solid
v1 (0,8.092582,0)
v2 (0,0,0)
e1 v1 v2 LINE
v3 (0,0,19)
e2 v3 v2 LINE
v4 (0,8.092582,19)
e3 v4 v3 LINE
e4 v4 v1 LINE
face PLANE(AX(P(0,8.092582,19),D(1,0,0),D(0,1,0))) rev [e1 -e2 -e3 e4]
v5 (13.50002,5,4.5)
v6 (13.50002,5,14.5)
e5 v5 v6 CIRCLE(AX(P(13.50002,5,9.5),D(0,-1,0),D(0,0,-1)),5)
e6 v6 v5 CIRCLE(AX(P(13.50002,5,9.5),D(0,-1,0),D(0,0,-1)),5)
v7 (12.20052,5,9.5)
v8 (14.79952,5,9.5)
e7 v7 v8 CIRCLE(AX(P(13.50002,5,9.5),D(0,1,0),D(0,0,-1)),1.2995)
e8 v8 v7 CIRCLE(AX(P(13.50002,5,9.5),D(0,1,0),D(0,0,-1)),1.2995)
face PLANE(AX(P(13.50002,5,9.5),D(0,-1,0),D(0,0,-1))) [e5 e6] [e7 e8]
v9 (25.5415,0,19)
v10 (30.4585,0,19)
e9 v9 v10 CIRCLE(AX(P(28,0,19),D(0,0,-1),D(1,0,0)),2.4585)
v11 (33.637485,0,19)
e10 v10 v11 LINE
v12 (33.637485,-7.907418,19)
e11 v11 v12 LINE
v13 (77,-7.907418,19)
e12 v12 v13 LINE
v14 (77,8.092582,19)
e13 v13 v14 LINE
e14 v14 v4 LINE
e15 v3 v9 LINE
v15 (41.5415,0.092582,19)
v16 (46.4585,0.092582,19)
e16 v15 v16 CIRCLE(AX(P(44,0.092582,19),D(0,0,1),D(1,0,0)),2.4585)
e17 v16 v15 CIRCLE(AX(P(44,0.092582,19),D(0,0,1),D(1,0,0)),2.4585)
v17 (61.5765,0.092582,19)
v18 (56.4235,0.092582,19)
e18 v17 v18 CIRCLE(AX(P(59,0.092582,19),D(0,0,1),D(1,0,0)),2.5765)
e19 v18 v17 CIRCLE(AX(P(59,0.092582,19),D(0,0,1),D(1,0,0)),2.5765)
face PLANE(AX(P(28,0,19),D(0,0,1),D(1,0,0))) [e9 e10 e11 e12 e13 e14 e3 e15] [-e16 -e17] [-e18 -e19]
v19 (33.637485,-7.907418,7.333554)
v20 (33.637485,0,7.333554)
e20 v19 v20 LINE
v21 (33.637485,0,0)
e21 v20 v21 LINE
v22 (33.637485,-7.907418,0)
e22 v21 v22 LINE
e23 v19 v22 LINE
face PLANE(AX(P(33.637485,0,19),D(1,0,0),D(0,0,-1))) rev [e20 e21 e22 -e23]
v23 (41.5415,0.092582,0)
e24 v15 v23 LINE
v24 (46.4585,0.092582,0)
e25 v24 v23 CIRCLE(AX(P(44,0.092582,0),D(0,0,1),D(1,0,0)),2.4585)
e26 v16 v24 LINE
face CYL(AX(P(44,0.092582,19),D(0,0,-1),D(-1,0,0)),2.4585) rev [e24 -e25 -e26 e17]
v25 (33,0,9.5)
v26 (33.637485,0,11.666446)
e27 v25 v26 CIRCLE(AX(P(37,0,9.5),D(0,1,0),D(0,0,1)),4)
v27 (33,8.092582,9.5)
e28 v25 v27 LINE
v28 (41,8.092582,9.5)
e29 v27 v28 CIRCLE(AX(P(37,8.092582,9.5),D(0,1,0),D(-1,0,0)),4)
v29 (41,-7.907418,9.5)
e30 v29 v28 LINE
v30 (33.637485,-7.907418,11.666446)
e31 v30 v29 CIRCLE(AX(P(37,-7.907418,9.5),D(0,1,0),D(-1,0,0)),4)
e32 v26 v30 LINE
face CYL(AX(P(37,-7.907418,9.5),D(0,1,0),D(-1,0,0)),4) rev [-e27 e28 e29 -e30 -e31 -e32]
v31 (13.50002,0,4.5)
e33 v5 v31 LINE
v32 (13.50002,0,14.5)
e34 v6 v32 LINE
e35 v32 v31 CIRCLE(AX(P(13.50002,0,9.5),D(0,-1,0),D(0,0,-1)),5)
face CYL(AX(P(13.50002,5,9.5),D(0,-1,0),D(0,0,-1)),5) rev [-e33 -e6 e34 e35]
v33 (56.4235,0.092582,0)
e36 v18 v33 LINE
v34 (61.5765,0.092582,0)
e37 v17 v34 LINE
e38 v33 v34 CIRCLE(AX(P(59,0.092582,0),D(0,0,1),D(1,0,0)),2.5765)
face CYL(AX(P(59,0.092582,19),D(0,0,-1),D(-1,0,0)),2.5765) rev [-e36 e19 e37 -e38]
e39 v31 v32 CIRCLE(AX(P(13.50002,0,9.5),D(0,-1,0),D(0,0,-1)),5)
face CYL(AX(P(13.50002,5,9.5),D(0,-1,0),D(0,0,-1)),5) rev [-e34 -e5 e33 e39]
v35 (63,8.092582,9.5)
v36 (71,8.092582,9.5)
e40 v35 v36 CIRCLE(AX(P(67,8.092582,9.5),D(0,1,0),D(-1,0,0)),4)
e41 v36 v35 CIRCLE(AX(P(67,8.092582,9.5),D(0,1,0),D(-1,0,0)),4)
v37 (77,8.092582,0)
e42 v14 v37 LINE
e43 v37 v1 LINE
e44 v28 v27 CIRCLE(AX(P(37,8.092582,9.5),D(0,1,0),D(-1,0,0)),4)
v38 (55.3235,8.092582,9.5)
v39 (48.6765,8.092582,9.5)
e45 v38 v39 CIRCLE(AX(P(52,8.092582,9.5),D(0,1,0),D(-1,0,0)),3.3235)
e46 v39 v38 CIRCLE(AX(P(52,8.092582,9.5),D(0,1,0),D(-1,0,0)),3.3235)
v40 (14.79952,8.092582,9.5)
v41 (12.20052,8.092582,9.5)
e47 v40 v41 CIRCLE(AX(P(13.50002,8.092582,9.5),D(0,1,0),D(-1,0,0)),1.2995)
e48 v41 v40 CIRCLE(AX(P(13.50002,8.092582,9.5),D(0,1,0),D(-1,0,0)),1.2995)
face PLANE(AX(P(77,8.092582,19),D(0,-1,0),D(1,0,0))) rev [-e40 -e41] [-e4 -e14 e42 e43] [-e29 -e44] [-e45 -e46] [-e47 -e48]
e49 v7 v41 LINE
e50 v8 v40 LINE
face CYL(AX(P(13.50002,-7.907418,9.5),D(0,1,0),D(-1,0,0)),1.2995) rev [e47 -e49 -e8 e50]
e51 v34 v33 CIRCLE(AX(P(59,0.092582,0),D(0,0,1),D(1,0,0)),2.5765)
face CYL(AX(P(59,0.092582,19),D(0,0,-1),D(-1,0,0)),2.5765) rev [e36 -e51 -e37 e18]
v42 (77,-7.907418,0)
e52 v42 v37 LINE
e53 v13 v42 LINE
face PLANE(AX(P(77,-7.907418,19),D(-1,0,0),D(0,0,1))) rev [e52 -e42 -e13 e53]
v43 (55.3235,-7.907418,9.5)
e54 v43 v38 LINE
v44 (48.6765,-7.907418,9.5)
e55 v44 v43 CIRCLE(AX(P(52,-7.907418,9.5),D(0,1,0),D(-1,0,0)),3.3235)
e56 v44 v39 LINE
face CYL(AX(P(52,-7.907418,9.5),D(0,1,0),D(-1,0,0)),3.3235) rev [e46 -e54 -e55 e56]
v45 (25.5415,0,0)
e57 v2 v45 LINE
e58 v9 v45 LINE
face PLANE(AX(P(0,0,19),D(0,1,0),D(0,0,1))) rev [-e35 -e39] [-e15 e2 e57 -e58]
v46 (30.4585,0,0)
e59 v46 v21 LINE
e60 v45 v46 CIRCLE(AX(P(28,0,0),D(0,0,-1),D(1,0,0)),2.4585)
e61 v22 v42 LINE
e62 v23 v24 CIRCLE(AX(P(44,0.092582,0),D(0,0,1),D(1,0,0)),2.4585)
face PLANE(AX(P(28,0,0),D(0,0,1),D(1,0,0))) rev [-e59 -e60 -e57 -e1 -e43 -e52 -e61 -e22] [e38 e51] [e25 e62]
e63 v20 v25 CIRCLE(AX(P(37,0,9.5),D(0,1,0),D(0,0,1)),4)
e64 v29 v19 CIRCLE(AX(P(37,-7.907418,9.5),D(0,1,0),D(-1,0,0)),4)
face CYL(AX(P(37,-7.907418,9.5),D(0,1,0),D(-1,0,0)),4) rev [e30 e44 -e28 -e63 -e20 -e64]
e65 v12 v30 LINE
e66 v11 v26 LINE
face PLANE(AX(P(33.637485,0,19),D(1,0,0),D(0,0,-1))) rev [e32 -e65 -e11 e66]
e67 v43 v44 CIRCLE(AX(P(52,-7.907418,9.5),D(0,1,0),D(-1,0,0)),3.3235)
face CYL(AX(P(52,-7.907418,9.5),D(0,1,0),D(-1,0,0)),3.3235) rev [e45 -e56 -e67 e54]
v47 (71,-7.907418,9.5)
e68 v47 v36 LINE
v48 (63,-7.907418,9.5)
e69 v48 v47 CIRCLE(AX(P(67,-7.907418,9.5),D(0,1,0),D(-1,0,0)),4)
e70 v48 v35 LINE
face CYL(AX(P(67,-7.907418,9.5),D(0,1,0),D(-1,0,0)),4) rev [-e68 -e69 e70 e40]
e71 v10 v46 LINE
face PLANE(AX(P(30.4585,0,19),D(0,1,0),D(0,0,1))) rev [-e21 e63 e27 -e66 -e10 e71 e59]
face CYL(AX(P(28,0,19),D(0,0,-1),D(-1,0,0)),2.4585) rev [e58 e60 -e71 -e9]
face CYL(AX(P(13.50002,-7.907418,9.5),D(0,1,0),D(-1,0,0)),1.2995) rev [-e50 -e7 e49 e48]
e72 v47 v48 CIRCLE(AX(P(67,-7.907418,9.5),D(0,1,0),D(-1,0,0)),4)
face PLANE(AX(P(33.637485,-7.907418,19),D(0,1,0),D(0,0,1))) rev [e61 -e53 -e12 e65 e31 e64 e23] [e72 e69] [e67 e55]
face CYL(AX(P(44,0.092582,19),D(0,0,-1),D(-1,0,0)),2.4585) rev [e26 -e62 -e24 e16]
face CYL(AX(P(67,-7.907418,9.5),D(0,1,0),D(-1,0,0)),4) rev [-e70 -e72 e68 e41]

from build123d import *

# Parameters (mm, degrees)
SKETCH1_R           = 2.5765
SKETCH1_R_2         = 2.4585
BOSS_EXTRUDE1_DEPTH = 19
SKETCH2_R           = 4
SKETCH2_R_2         = 3.3235
SKETCH2_R_3         = 1.2995
CUT_EXTRUDE1_DEPTH  = 81.907354425
SKETCH3_R           = 5
CUT_EXTRUDE2_DEPTH  = 5


with BuildPart() as part:
    # Sketch1 → Boss-Extrude1 (new body)
    with BuildSketch(Plane.XY):
        with BuildLine():
            Line((0, 0), (25.5415, 0))
            ThreePointArc((25.5415, 0), (28, 2.4585), (30.4585, 0))
            Line((30.4585, 0), (33.63748457, 0))
            Line((33.63748457, 0), (33.63748457, -7.90741809))
            Line((33.63748457, -7.90741809), (77, -7.90741809))
            Line((77, -7.90741809), (77, 8.09258191))
            Line((77, 8.09258191), (0, 8.09258191))
            Line((0, 8.09258191), (0, 0))
        make_face()
        with Locations((59, 0.09258191)):
            Circle(SKETCH1_R, mode=Mode.SUBTRACT)
        with Locations((44, 0.09258191)):
            Circle(SKETCH1_R_2, mode=Mode.SUBTRACT)
    extrude(amount=BOSS_EXTRUDE1_DEPTH)

    # Sketch2 → Cut-Extrude1 (cut, through all)
    with BuildSketch(Plane(origin=(0, 8.09258191, 0), x_dir=(1, 0, 0), z_dir=(0, 1, 0))):
        with Locations(Location((67, -9.5, 0), (0, 0, 180))):
            Circle(SKETCH2_R)
        with Locations(Location((52, -9.5, 0), (0, 0, 180))):
            Circle(SKETCH2_R_2)
        with Locations(Location((37, -9.5, 0), (0, 0, 180))):
            Circle(SKETCH2_R)
        with Locations(Location((13.50002, -9.5, 0), (0, 0, 180))):
            Circle(SKETCH2_R_3)
    extrude(amount=-CUT_EXTRUDE1_DEPTH, mode=Mode.SUBTRACT)

    # Sketch3 → Cut-Extrude2 (cut)
    with BuildSketch(Plane(origin=(0, 0, 0), x_dir=(-1, 0, 0), z_dir=(0, -1, 0))):
        with Locations(Location((-13.50002, -9.5, 0), (0, 0, 90))):
            Circle(SKETCH3_R)
    extrude(amount=-CUT_EXTRUDE2_DEPTH, mode=Mode.SUBTRACT)


solid = part.part
